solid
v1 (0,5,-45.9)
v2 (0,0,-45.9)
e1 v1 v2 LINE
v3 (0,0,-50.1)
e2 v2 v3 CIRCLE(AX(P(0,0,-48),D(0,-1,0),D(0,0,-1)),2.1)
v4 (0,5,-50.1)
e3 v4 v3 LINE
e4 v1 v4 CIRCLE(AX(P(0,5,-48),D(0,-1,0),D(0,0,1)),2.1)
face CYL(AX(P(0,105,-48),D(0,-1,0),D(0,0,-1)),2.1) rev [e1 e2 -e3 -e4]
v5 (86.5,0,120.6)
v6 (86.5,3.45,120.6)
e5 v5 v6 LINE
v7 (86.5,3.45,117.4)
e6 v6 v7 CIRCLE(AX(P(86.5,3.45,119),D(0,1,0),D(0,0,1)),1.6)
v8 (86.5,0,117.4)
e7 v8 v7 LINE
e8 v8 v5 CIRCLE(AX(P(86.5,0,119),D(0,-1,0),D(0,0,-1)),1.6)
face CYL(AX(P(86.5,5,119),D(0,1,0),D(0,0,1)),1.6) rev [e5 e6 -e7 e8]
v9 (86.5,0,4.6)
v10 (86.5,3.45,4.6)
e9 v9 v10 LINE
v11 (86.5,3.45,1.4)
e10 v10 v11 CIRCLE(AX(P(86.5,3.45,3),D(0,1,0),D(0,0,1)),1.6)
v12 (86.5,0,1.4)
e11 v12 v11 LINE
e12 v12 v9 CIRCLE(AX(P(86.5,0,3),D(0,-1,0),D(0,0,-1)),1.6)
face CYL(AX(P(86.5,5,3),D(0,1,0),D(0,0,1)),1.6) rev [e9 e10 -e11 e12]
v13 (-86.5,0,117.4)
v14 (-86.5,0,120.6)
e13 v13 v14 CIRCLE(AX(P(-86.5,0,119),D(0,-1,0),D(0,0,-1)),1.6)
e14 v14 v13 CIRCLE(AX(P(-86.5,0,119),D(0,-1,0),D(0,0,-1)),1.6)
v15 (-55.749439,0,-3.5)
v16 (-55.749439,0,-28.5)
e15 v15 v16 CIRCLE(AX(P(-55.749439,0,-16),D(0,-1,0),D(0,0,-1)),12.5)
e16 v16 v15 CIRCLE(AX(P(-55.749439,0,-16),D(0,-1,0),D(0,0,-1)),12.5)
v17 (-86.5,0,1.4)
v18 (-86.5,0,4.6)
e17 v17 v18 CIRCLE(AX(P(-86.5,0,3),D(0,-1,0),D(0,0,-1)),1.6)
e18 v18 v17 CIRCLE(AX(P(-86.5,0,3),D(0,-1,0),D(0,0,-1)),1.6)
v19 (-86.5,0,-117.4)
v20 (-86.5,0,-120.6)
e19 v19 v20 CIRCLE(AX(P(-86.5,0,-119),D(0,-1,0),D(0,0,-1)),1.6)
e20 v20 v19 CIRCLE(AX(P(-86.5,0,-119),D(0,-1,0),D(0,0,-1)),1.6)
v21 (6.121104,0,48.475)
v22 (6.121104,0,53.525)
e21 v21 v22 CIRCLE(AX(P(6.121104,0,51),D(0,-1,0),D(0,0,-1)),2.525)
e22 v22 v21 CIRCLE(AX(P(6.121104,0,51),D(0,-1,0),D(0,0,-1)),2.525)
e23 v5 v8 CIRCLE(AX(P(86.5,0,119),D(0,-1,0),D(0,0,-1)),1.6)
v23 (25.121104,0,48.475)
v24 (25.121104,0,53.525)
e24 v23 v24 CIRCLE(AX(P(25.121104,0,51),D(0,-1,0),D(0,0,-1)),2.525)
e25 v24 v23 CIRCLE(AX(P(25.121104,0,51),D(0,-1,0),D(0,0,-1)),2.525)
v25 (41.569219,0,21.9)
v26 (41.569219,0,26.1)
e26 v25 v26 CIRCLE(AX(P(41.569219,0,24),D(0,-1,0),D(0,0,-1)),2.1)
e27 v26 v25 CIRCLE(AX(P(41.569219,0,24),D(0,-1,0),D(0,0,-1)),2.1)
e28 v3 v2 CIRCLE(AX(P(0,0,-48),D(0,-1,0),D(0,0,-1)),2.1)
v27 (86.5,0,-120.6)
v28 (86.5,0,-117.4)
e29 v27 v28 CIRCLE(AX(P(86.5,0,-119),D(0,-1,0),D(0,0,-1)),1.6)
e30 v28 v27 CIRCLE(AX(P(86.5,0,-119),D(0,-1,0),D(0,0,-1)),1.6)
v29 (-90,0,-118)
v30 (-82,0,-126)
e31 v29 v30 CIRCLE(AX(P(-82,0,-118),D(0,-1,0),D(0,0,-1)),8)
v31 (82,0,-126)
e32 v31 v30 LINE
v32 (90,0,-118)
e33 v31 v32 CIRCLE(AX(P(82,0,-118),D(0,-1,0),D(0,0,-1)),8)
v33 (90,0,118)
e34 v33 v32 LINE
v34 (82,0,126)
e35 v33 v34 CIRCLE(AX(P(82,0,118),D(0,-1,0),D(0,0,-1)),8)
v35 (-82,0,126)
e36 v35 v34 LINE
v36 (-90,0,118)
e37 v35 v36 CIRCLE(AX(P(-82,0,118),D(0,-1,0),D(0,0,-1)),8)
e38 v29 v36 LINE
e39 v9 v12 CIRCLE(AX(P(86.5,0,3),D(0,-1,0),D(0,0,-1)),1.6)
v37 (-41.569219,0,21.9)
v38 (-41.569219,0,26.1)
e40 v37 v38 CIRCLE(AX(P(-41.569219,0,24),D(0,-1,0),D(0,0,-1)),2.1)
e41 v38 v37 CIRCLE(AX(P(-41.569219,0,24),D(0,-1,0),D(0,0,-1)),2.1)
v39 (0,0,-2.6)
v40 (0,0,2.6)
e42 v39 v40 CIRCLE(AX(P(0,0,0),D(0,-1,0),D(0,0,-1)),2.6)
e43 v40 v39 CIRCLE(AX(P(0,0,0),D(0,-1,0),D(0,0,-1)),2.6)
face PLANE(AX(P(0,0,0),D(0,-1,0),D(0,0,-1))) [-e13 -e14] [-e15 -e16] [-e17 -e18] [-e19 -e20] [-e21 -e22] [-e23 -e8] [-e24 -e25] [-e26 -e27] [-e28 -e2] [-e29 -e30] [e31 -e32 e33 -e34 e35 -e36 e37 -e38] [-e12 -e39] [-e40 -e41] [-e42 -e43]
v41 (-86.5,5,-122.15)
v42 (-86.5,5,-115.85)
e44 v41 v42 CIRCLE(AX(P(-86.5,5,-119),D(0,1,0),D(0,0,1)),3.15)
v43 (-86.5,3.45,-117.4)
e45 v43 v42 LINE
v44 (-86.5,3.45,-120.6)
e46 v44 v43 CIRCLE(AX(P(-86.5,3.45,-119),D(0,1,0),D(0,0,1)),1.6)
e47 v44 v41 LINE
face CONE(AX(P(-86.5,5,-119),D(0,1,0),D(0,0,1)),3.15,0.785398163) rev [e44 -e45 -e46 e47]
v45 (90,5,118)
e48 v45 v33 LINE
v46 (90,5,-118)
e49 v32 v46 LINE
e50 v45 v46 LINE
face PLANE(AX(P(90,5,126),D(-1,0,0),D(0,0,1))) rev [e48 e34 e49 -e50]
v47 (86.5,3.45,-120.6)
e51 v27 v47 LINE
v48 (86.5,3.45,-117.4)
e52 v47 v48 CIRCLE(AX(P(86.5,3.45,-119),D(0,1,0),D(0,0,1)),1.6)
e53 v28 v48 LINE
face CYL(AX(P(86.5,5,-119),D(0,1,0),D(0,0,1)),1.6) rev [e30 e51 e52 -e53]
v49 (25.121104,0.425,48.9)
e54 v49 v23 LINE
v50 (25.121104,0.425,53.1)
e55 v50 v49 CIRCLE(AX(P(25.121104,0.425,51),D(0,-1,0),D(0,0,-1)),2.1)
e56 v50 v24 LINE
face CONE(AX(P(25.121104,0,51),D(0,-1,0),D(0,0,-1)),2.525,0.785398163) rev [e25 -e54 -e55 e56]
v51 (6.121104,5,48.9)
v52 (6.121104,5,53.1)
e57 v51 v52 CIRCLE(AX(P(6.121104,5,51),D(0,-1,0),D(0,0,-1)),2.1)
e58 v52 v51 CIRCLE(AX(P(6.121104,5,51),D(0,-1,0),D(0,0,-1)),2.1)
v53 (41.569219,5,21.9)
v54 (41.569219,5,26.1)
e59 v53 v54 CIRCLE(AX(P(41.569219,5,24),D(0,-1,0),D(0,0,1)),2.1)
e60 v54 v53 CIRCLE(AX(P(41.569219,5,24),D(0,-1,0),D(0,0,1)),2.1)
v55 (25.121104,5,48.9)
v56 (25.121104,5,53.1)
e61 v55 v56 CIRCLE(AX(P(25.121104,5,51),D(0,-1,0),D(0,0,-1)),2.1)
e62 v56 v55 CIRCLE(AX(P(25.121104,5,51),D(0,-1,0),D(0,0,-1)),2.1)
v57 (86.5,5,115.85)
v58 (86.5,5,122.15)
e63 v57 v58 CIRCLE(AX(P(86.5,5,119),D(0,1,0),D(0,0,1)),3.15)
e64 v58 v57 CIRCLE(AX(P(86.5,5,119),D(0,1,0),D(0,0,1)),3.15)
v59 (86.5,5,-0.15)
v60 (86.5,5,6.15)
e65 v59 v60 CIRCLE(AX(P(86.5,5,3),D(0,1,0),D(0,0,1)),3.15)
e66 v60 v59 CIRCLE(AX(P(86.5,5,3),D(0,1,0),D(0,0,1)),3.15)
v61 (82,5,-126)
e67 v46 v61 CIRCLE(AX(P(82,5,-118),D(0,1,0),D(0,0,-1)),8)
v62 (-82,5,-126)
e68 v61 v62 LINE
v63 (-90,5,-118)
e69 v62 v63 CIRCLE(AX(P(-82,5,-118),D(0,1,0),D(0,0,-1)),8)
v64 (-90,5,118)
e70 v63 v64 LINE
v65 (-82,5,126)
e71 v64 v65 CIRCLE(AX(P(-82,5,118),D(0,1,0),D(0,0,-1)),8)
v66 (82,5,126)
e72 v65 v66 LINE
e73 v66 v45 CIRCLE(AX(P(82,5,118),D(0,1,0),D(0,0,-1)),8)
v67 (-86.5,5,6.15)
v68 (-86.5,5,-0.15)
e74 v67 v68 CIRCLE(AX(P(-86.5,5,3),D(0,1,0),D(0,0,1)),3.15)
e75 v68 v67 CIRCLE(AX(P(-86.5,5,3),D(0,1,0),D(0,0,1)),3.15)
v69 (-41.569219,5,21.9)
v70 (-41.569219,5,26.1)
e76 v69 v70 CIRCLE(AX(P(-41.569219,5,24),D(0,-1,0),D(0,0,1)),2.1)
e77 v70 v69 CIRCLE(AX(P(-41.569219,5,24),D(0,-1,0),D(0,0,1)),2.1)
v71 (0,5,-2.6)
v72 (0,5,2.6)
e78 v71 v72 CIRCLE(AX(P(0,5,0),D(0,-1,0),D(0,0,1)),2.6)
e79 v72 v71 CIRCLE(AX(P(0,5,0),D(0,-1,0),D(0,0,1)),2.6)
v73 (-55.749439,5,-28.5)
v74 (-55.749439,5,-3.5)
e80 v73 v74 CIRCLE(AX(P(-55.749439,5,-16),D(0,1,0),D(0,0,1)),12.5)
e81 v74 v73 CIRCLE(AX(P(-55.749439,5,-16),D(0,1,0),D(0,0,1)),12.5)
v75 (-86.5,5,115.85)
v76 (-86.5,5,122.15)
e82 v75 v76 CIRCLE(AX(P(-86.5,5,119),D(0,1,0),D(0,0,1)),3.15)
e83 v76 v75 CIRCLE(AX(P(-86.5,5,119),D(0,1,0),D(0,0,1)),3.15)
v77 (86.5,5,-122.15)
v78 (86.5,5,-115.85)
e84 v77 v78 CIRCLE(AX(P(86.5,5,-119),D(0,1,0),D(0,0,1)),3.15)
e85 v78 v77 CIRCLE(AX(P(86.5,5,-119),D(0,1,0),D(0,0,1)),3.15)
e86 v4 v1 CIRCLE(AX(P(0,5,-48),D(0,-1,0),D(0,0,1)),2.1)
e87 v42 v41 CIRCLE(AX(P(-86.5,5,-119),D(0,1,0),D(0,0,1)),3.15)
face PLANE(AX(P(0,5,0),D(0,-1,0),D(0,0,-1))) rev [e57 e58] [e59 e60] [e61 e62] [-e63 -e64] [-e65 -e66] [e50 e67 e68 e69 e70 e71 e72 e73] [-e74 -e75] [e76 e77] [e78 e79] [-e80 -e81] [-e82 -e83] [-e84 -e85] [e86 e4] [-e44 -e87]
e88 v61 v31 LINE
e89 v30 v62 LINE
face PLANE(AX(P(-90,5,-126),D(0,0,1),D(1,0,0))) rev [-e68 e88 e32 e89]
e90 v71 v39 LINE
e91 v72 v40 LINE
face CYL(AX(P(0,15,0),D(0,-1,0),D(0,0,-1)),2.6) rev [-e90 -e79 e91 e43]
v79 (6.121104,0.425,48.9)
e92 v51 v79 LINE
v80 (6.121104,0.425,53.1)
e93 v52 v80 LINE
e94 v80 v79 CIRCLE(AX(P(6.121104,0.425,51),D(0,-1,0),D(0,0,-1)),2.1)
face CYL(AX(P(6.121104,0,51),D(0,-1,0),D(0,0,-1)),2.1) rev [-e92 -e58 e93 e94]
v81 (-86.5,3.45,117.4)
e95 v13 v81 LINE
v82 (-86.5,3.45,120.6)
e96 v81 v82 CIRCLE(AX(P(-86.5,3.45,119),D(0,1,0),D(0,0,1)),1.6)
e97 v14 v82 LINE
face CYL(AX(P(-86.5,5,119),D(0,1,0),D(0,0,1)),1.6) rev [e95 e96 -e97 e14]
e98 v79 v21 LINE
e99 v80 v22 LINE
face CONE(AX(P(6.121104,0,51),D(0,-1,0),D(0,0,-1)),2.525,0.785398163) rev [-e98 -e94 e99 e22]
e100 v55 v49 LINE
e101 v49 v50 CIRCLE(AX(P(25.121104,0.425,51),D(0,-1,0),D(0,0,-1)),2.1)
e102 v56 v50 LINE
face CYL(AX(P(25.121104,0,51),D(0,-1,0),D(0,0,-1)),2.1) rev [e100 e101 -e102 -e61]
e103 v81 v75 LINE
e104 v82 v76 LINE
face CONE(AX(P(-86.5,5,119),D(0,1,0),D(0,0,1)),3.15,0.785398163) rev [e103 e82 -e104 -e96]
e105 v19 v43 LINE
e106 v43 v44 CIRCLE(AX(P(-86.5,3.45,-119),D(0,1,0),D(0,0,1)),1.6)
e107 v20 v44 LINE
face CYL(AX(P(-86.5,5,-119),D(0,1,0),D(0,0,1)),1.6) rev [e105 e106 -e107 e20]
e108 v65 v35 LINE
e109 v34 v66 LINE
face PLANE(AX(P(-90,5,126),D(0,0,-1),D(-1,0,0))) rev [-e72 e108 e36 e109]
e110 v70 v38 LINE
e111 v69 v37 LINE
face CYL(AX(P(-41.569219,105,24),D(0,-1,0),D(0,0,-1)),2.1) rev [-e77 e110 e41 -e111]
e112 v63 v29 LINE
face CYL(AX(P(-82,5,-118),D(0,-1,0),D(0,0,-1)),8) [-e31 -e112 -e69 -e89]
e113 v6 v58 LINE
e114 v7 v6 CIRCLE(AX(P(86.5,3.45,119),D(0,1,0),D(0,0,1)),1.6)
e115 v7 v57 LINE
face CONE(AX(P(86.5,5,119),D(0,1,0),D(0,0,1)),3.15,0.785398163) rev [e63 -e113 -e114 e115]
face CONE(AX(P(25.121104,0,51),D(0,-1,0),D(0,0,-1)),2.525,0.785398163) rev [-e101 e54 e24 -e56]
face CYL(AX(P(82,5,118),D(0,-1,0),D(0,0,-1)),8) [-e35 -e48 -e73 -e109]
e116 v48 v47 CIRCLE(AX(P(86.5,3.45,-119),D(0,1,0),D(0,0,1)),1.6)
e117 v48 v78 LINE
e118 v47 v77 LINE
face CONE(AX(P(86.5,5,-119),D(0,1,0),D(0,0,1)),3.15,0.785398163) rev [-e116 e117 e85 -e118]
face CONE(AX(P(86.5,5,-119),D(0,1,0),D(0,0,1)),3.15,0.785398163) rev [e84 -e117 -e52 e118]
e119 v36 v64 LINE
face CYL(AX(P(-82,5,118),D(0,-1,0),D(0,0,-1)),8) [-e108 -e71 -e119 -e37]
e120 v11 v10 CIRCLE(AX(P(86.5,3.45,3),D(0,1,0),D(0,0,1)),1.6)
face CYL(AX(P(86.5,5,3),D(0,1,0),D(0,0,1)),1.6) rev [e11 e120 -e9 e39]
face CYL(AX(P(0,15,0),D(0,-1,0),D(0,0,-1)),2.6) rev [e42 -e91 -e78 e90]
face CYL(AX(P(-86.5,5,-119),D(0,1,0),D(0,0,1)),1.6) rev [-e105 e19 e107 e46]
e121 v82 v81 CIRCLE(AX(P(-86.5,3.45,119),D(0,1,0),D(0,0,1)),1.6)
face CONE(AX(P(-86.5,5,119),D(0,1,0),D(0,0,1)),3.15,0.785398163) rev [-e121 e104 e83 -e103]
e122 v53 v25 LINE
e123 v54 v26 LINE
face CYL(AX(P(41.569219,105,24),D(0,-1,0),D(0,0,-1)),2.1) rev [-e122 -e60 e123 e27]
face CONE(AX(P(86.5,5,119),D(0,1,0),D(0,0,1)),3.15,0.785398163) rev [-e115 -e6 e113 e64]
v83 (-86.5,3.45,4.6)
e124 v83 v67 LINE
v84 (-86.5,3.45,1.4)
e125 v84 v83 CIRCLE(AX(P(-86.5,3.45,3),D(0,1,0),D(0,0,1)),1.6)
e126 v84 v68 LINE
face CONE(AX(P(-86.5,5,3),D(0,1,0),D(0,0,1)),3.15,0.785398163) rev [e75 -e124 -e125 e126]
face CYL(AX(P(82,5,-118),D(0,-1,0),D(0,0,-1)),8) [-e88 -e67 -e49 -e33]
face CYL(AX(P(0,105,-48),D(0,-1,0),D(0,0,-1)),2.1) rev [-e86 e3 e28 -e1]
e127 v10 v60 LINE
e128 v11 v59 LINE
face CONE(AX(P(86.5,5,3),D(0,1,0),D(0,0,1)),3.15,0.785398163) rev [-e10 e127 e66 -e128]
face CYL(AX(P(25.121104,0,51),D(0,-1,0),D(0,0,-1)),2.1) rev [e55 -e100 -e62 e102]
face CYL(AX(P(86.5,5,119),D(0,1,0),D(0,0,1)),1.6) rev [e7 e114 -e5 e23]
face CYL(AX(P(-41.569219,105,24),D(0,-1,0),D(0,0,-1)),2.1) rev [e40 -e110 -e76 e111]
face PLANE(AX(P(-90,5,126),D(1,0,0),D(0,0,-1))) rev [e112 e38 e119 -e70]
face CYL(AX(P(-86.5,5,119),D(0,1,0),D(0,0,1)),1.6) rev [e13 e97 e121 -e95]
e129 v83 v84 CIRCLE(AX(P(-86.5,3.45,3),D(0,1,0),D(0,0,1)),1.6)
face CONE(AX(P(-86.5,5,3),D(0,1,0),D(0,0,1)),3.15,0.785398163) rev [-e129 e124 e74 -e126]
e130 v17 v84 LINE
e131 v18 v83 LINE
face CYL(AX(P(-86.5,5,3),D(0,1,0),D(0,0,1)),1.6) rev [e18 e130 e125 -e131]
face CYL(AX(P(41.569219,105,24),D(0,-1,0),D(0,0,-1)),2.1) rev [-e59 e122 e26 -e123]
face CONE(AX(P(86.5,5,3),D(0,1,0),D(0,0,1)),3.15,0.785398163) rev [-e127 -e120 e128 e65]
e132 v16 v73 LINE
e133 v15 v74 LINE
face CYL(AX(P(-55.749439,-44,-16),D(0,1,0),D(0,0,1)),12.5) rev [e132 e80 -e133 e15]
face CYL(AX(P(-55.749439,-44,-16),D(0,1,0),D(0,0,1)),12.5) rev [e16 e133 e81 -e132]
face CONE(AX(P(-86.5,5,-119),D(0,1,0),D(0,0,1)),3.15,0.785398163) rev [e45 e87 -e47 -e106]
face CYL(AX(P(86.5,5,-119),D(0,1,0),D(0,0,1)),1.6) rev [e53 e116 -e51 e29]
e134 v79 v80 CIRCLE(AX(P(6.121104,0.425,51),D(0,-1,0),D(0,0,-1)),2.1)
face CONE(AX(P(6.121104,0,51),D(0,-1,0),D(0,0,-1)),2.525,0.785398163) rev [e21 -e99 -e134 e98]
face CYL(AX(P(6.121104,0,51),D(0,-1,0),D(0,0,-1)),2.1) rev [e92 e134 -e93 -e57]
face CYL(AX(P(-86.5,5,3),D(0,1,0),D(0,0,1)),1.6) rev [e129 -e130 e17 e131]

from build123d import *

# Parameters (mm, degrees)
SKETCH1_W                                       = 180
SKETCH1_H                                       = 252
BOSS_EXTRUDE1_DEPTH                             = 5
SKETCH2_R                                       = 70
BOSS_EXTRUDE2_DEPTH                             = 50
DOME1_FACE_RADIUS                               = 70
DOME1_HEIGHT                                    = 50
SKETCH3_R                                       = 2.1
CUT_EXTRUDE1_DEPTH                              = 188.085541932
CSK_FOR_M3_FLAT_HEAD_MACHINE_SCREW1_D           = 3.2
CSK_FOR_M3_FLAT_HEAD_MACHINE_SCREW1_DEPTH       = 8.5
CSK_FOR_M3_FLAT_HEAD_MACHINE_SCREW1_CSINK_D     = 6.3
CSK_FOR_M3_FLAT_HEAD_MACHINE_SCREW1_CSINK_ANGLE = 90
CSK_FOR_M3_FLAT_HEAD_MACHINE_SCREW1_TIP         = 0.96137699
SKETCH7_R                                       = 2.6
CUT_EXTRUDE3_DEPTH                              = 15
SKETCH9_W                                       = 180
SKETCH9_H                                       = 252
CUT_EXTRUDE4_DEPTH                              = 168
SKETCH11_R                                      = 12.5
CUT_EXTRUDE5_DEPTH                              = 49
FILLET1_R                                       = 8
M5_TAPPED_HOLE1_D                               = 4.2
M5_TAPPED_HOLE1_DEPTH                           = 14
M5_TAPPED_HOLE1_CSINK_D                         = 5.05
M5_TAPPED_HOLE1_CSINK_ANGLE                     = 90
M5_TAPPED_HOLE1_TIP                             = 1.2618073


with BuildPart() as part:
    # Sketch1 → Boss-Extrude1 (new body)
    with BuildSketch(Plane(origin=(0, 0, 0), x_dir=(1, 0, 0), z_dir=(0, 1, 0))):
        Rectangle(SKETCH1_W, SKETCH1_H)
    extrude(amount=BOSS_EXTRUDE1_DEPTH)

    # Sketch2 → Boss-Extrude2 (add)
    with BuildSketch(Plane(origin=(0, 5, 0), x_dir=(1, 0, 0), z_dir=(0, 1, 0))):
        with Locations(Location((0, 0, 0), (0, 0, 270))):
            Circle(SKETCH2_R)
    extrude(amount=BOSS_EXTRUDE2_DEPTH)

    # Dome1: a dome of height H over a round flat face of radius A is a cap of a sphere of radius (A * A + H * H) / (2 * H)
    dome1_r = (DOME1_FACE_RADIUS * DOME1_FACE_RADIUS + DOME1_HEIGHT * DOME1_HEIGHT) / (2 * DOME1_HEIGHT)
    dome1_base = Plane((0, 55, 0), z_dir=(0, 1, 0))
    with Locations(dome1_base.offset(DOME1_HEIGHT - dome1_r)):
        dome1_ball = Sphere(dome1_r, mode=Mode.PRIVATE)
    add(split(dome1_ball, bisect_by=dome1_base, keep=Keep.TOP, mode=Mode.PRIVATE))

    # Sketch3 → Cut-Extrude1 (cut, through all)
    with BuildSketch(Plane.XZ):
        with Locations(Location((0, -48, 0), (0, 0, 270))):
            Circle(SKETCH3_R)
        with Locations(Location((-41.569219382, 24, 0), (0, 0, 270))):
            Circle(SKETCH3_R)
        with Locations(Location((41.569219382, 24, 0), (0, 0, 270))):
            Circle(SKETCH3_R)
    extrude(amount=-CUT_EXTRUDE1_DEPTH, mode=Mode.SUBTRACT)

    # CSK for M3 Flat Head Machine Screw1
    with Locations(Plane(origin=(0, 5, 0), x_dir=(1, 0, 0), z_dir=(0, 1, 0))):
        with Locations((86.5, 119), (86.5, -3), (86.5, -119), (-86.5, -119), (-86.5, -3), (-86.5, 119)):
            CounterSinkHole(CSK_FOR_M3_FLAT_HEAD_MACHINE_SCREW1_D / 2, CSK_FOR_M3_FLAT_HEAD_MACHINE_SCREW1_CSINK_D / 2, depth=CSK_FOR_M3_FLAT_HEAD_MACHINE_SCREW1_DEPTH, counter_sink_angle=CSK_FOR_M3_FLAT_HEAD_MACHINE_SCREW1_CSINK_ANGLE)
            with Locations((0, 0, -(CSK_FOR_M3_FLAT_HEAD_MACHINE_SCREW1_DEPTH + CSK_FOR_M3_FLAT_HEAD_MACHINE_SCREW1_TIP / 2))):  # 118° drill point
                Cone(0, CSK_FOR_M3_FLAT_HEAD_MACHINE_SCREW1_D / 2, CSK_FOR_M3_FLAT_HEAD_MACHINE_SCREW1_TIP, mode=Mode.SUBTRACT)

    # Sketch7 → Cut-Extrude3 (cut)
    with BuildSketch(Plane.XZ):
        with Locations(Location((0, 0, 0), (0, 0, 270))):
            Circle(SKETCH7_R)
    extrude(amount=-CUT_EXTRUDE3_DEPTH, mode=Mode.SUBTRACT)

    # Sketch9 → Cut-Extrude4 (cut)
    with BuildSketch(Plane(origin=(0, 5, 0), x_dir=(1, 0, 0), z_dir=(0, 1, 0))):
        Rectangle(SKETCH9_W, SKETCH9_H)
    extrude(amount=CUT_EXTRUDE4_DEPTH, mode=Mode.SUBTRACT)

    # Sketch11 → Cut-Extrude5 (cut)
    with BuildSketch(Plane(origin=(0, 5, 0), x_dir=(1, 0, 0), z_dir=(0, 1, 0))):
        with Locations(Location((-55.749439459, 16, 0), (0, 0, 270))):
            Circle(SKETCH11_R)
    extrude(amount=-CUT_EXTRUDE5_DEPTH, mode=Mode.SUBTRACT)

    # Fillet1
    fillet1_edges = [part.edges().sort_by_distance(p)[0] for p in [
        (90, 2.5, 126),
        (-90, 2.5, 126),
        (-90, 2.5, -126),
        (90, 2.5, -126),
    ]]
    fillet(fillet1_edges, radius=FILLET1_R)

    # M5 Tapped Hole1
    with Locations(Plane(origin=(0, 0, 0), x_dir=(-1, 0, 0), z_dir=(0, -1, 0))):
        with Locations((-25.121103622, -51), (-6.121103622, -51)):
            CounterSinkHole(M5_TAPPED_HOLE1_D / 2, M5_TAPPED_HOLE1_CSINK_D / 2, depth=M5_TAPPED_HOLE1_DEPTH, counter_sink_angle=M5_TAPPED_HOLE1_CSINK_ANGLE)
            with Locations((0, 0, -(M5_TAPPED_HOLE1_DEPTH + M5_TAPPED_HOLE1_TIP / 2))):  # 118° drill point
                Cone(0, M5_TAPPED_HOLE1_D / 2, M5_TAPPED_HOLE1_TIP, mode=Mode.SUBTRACT)


solid = part.part
